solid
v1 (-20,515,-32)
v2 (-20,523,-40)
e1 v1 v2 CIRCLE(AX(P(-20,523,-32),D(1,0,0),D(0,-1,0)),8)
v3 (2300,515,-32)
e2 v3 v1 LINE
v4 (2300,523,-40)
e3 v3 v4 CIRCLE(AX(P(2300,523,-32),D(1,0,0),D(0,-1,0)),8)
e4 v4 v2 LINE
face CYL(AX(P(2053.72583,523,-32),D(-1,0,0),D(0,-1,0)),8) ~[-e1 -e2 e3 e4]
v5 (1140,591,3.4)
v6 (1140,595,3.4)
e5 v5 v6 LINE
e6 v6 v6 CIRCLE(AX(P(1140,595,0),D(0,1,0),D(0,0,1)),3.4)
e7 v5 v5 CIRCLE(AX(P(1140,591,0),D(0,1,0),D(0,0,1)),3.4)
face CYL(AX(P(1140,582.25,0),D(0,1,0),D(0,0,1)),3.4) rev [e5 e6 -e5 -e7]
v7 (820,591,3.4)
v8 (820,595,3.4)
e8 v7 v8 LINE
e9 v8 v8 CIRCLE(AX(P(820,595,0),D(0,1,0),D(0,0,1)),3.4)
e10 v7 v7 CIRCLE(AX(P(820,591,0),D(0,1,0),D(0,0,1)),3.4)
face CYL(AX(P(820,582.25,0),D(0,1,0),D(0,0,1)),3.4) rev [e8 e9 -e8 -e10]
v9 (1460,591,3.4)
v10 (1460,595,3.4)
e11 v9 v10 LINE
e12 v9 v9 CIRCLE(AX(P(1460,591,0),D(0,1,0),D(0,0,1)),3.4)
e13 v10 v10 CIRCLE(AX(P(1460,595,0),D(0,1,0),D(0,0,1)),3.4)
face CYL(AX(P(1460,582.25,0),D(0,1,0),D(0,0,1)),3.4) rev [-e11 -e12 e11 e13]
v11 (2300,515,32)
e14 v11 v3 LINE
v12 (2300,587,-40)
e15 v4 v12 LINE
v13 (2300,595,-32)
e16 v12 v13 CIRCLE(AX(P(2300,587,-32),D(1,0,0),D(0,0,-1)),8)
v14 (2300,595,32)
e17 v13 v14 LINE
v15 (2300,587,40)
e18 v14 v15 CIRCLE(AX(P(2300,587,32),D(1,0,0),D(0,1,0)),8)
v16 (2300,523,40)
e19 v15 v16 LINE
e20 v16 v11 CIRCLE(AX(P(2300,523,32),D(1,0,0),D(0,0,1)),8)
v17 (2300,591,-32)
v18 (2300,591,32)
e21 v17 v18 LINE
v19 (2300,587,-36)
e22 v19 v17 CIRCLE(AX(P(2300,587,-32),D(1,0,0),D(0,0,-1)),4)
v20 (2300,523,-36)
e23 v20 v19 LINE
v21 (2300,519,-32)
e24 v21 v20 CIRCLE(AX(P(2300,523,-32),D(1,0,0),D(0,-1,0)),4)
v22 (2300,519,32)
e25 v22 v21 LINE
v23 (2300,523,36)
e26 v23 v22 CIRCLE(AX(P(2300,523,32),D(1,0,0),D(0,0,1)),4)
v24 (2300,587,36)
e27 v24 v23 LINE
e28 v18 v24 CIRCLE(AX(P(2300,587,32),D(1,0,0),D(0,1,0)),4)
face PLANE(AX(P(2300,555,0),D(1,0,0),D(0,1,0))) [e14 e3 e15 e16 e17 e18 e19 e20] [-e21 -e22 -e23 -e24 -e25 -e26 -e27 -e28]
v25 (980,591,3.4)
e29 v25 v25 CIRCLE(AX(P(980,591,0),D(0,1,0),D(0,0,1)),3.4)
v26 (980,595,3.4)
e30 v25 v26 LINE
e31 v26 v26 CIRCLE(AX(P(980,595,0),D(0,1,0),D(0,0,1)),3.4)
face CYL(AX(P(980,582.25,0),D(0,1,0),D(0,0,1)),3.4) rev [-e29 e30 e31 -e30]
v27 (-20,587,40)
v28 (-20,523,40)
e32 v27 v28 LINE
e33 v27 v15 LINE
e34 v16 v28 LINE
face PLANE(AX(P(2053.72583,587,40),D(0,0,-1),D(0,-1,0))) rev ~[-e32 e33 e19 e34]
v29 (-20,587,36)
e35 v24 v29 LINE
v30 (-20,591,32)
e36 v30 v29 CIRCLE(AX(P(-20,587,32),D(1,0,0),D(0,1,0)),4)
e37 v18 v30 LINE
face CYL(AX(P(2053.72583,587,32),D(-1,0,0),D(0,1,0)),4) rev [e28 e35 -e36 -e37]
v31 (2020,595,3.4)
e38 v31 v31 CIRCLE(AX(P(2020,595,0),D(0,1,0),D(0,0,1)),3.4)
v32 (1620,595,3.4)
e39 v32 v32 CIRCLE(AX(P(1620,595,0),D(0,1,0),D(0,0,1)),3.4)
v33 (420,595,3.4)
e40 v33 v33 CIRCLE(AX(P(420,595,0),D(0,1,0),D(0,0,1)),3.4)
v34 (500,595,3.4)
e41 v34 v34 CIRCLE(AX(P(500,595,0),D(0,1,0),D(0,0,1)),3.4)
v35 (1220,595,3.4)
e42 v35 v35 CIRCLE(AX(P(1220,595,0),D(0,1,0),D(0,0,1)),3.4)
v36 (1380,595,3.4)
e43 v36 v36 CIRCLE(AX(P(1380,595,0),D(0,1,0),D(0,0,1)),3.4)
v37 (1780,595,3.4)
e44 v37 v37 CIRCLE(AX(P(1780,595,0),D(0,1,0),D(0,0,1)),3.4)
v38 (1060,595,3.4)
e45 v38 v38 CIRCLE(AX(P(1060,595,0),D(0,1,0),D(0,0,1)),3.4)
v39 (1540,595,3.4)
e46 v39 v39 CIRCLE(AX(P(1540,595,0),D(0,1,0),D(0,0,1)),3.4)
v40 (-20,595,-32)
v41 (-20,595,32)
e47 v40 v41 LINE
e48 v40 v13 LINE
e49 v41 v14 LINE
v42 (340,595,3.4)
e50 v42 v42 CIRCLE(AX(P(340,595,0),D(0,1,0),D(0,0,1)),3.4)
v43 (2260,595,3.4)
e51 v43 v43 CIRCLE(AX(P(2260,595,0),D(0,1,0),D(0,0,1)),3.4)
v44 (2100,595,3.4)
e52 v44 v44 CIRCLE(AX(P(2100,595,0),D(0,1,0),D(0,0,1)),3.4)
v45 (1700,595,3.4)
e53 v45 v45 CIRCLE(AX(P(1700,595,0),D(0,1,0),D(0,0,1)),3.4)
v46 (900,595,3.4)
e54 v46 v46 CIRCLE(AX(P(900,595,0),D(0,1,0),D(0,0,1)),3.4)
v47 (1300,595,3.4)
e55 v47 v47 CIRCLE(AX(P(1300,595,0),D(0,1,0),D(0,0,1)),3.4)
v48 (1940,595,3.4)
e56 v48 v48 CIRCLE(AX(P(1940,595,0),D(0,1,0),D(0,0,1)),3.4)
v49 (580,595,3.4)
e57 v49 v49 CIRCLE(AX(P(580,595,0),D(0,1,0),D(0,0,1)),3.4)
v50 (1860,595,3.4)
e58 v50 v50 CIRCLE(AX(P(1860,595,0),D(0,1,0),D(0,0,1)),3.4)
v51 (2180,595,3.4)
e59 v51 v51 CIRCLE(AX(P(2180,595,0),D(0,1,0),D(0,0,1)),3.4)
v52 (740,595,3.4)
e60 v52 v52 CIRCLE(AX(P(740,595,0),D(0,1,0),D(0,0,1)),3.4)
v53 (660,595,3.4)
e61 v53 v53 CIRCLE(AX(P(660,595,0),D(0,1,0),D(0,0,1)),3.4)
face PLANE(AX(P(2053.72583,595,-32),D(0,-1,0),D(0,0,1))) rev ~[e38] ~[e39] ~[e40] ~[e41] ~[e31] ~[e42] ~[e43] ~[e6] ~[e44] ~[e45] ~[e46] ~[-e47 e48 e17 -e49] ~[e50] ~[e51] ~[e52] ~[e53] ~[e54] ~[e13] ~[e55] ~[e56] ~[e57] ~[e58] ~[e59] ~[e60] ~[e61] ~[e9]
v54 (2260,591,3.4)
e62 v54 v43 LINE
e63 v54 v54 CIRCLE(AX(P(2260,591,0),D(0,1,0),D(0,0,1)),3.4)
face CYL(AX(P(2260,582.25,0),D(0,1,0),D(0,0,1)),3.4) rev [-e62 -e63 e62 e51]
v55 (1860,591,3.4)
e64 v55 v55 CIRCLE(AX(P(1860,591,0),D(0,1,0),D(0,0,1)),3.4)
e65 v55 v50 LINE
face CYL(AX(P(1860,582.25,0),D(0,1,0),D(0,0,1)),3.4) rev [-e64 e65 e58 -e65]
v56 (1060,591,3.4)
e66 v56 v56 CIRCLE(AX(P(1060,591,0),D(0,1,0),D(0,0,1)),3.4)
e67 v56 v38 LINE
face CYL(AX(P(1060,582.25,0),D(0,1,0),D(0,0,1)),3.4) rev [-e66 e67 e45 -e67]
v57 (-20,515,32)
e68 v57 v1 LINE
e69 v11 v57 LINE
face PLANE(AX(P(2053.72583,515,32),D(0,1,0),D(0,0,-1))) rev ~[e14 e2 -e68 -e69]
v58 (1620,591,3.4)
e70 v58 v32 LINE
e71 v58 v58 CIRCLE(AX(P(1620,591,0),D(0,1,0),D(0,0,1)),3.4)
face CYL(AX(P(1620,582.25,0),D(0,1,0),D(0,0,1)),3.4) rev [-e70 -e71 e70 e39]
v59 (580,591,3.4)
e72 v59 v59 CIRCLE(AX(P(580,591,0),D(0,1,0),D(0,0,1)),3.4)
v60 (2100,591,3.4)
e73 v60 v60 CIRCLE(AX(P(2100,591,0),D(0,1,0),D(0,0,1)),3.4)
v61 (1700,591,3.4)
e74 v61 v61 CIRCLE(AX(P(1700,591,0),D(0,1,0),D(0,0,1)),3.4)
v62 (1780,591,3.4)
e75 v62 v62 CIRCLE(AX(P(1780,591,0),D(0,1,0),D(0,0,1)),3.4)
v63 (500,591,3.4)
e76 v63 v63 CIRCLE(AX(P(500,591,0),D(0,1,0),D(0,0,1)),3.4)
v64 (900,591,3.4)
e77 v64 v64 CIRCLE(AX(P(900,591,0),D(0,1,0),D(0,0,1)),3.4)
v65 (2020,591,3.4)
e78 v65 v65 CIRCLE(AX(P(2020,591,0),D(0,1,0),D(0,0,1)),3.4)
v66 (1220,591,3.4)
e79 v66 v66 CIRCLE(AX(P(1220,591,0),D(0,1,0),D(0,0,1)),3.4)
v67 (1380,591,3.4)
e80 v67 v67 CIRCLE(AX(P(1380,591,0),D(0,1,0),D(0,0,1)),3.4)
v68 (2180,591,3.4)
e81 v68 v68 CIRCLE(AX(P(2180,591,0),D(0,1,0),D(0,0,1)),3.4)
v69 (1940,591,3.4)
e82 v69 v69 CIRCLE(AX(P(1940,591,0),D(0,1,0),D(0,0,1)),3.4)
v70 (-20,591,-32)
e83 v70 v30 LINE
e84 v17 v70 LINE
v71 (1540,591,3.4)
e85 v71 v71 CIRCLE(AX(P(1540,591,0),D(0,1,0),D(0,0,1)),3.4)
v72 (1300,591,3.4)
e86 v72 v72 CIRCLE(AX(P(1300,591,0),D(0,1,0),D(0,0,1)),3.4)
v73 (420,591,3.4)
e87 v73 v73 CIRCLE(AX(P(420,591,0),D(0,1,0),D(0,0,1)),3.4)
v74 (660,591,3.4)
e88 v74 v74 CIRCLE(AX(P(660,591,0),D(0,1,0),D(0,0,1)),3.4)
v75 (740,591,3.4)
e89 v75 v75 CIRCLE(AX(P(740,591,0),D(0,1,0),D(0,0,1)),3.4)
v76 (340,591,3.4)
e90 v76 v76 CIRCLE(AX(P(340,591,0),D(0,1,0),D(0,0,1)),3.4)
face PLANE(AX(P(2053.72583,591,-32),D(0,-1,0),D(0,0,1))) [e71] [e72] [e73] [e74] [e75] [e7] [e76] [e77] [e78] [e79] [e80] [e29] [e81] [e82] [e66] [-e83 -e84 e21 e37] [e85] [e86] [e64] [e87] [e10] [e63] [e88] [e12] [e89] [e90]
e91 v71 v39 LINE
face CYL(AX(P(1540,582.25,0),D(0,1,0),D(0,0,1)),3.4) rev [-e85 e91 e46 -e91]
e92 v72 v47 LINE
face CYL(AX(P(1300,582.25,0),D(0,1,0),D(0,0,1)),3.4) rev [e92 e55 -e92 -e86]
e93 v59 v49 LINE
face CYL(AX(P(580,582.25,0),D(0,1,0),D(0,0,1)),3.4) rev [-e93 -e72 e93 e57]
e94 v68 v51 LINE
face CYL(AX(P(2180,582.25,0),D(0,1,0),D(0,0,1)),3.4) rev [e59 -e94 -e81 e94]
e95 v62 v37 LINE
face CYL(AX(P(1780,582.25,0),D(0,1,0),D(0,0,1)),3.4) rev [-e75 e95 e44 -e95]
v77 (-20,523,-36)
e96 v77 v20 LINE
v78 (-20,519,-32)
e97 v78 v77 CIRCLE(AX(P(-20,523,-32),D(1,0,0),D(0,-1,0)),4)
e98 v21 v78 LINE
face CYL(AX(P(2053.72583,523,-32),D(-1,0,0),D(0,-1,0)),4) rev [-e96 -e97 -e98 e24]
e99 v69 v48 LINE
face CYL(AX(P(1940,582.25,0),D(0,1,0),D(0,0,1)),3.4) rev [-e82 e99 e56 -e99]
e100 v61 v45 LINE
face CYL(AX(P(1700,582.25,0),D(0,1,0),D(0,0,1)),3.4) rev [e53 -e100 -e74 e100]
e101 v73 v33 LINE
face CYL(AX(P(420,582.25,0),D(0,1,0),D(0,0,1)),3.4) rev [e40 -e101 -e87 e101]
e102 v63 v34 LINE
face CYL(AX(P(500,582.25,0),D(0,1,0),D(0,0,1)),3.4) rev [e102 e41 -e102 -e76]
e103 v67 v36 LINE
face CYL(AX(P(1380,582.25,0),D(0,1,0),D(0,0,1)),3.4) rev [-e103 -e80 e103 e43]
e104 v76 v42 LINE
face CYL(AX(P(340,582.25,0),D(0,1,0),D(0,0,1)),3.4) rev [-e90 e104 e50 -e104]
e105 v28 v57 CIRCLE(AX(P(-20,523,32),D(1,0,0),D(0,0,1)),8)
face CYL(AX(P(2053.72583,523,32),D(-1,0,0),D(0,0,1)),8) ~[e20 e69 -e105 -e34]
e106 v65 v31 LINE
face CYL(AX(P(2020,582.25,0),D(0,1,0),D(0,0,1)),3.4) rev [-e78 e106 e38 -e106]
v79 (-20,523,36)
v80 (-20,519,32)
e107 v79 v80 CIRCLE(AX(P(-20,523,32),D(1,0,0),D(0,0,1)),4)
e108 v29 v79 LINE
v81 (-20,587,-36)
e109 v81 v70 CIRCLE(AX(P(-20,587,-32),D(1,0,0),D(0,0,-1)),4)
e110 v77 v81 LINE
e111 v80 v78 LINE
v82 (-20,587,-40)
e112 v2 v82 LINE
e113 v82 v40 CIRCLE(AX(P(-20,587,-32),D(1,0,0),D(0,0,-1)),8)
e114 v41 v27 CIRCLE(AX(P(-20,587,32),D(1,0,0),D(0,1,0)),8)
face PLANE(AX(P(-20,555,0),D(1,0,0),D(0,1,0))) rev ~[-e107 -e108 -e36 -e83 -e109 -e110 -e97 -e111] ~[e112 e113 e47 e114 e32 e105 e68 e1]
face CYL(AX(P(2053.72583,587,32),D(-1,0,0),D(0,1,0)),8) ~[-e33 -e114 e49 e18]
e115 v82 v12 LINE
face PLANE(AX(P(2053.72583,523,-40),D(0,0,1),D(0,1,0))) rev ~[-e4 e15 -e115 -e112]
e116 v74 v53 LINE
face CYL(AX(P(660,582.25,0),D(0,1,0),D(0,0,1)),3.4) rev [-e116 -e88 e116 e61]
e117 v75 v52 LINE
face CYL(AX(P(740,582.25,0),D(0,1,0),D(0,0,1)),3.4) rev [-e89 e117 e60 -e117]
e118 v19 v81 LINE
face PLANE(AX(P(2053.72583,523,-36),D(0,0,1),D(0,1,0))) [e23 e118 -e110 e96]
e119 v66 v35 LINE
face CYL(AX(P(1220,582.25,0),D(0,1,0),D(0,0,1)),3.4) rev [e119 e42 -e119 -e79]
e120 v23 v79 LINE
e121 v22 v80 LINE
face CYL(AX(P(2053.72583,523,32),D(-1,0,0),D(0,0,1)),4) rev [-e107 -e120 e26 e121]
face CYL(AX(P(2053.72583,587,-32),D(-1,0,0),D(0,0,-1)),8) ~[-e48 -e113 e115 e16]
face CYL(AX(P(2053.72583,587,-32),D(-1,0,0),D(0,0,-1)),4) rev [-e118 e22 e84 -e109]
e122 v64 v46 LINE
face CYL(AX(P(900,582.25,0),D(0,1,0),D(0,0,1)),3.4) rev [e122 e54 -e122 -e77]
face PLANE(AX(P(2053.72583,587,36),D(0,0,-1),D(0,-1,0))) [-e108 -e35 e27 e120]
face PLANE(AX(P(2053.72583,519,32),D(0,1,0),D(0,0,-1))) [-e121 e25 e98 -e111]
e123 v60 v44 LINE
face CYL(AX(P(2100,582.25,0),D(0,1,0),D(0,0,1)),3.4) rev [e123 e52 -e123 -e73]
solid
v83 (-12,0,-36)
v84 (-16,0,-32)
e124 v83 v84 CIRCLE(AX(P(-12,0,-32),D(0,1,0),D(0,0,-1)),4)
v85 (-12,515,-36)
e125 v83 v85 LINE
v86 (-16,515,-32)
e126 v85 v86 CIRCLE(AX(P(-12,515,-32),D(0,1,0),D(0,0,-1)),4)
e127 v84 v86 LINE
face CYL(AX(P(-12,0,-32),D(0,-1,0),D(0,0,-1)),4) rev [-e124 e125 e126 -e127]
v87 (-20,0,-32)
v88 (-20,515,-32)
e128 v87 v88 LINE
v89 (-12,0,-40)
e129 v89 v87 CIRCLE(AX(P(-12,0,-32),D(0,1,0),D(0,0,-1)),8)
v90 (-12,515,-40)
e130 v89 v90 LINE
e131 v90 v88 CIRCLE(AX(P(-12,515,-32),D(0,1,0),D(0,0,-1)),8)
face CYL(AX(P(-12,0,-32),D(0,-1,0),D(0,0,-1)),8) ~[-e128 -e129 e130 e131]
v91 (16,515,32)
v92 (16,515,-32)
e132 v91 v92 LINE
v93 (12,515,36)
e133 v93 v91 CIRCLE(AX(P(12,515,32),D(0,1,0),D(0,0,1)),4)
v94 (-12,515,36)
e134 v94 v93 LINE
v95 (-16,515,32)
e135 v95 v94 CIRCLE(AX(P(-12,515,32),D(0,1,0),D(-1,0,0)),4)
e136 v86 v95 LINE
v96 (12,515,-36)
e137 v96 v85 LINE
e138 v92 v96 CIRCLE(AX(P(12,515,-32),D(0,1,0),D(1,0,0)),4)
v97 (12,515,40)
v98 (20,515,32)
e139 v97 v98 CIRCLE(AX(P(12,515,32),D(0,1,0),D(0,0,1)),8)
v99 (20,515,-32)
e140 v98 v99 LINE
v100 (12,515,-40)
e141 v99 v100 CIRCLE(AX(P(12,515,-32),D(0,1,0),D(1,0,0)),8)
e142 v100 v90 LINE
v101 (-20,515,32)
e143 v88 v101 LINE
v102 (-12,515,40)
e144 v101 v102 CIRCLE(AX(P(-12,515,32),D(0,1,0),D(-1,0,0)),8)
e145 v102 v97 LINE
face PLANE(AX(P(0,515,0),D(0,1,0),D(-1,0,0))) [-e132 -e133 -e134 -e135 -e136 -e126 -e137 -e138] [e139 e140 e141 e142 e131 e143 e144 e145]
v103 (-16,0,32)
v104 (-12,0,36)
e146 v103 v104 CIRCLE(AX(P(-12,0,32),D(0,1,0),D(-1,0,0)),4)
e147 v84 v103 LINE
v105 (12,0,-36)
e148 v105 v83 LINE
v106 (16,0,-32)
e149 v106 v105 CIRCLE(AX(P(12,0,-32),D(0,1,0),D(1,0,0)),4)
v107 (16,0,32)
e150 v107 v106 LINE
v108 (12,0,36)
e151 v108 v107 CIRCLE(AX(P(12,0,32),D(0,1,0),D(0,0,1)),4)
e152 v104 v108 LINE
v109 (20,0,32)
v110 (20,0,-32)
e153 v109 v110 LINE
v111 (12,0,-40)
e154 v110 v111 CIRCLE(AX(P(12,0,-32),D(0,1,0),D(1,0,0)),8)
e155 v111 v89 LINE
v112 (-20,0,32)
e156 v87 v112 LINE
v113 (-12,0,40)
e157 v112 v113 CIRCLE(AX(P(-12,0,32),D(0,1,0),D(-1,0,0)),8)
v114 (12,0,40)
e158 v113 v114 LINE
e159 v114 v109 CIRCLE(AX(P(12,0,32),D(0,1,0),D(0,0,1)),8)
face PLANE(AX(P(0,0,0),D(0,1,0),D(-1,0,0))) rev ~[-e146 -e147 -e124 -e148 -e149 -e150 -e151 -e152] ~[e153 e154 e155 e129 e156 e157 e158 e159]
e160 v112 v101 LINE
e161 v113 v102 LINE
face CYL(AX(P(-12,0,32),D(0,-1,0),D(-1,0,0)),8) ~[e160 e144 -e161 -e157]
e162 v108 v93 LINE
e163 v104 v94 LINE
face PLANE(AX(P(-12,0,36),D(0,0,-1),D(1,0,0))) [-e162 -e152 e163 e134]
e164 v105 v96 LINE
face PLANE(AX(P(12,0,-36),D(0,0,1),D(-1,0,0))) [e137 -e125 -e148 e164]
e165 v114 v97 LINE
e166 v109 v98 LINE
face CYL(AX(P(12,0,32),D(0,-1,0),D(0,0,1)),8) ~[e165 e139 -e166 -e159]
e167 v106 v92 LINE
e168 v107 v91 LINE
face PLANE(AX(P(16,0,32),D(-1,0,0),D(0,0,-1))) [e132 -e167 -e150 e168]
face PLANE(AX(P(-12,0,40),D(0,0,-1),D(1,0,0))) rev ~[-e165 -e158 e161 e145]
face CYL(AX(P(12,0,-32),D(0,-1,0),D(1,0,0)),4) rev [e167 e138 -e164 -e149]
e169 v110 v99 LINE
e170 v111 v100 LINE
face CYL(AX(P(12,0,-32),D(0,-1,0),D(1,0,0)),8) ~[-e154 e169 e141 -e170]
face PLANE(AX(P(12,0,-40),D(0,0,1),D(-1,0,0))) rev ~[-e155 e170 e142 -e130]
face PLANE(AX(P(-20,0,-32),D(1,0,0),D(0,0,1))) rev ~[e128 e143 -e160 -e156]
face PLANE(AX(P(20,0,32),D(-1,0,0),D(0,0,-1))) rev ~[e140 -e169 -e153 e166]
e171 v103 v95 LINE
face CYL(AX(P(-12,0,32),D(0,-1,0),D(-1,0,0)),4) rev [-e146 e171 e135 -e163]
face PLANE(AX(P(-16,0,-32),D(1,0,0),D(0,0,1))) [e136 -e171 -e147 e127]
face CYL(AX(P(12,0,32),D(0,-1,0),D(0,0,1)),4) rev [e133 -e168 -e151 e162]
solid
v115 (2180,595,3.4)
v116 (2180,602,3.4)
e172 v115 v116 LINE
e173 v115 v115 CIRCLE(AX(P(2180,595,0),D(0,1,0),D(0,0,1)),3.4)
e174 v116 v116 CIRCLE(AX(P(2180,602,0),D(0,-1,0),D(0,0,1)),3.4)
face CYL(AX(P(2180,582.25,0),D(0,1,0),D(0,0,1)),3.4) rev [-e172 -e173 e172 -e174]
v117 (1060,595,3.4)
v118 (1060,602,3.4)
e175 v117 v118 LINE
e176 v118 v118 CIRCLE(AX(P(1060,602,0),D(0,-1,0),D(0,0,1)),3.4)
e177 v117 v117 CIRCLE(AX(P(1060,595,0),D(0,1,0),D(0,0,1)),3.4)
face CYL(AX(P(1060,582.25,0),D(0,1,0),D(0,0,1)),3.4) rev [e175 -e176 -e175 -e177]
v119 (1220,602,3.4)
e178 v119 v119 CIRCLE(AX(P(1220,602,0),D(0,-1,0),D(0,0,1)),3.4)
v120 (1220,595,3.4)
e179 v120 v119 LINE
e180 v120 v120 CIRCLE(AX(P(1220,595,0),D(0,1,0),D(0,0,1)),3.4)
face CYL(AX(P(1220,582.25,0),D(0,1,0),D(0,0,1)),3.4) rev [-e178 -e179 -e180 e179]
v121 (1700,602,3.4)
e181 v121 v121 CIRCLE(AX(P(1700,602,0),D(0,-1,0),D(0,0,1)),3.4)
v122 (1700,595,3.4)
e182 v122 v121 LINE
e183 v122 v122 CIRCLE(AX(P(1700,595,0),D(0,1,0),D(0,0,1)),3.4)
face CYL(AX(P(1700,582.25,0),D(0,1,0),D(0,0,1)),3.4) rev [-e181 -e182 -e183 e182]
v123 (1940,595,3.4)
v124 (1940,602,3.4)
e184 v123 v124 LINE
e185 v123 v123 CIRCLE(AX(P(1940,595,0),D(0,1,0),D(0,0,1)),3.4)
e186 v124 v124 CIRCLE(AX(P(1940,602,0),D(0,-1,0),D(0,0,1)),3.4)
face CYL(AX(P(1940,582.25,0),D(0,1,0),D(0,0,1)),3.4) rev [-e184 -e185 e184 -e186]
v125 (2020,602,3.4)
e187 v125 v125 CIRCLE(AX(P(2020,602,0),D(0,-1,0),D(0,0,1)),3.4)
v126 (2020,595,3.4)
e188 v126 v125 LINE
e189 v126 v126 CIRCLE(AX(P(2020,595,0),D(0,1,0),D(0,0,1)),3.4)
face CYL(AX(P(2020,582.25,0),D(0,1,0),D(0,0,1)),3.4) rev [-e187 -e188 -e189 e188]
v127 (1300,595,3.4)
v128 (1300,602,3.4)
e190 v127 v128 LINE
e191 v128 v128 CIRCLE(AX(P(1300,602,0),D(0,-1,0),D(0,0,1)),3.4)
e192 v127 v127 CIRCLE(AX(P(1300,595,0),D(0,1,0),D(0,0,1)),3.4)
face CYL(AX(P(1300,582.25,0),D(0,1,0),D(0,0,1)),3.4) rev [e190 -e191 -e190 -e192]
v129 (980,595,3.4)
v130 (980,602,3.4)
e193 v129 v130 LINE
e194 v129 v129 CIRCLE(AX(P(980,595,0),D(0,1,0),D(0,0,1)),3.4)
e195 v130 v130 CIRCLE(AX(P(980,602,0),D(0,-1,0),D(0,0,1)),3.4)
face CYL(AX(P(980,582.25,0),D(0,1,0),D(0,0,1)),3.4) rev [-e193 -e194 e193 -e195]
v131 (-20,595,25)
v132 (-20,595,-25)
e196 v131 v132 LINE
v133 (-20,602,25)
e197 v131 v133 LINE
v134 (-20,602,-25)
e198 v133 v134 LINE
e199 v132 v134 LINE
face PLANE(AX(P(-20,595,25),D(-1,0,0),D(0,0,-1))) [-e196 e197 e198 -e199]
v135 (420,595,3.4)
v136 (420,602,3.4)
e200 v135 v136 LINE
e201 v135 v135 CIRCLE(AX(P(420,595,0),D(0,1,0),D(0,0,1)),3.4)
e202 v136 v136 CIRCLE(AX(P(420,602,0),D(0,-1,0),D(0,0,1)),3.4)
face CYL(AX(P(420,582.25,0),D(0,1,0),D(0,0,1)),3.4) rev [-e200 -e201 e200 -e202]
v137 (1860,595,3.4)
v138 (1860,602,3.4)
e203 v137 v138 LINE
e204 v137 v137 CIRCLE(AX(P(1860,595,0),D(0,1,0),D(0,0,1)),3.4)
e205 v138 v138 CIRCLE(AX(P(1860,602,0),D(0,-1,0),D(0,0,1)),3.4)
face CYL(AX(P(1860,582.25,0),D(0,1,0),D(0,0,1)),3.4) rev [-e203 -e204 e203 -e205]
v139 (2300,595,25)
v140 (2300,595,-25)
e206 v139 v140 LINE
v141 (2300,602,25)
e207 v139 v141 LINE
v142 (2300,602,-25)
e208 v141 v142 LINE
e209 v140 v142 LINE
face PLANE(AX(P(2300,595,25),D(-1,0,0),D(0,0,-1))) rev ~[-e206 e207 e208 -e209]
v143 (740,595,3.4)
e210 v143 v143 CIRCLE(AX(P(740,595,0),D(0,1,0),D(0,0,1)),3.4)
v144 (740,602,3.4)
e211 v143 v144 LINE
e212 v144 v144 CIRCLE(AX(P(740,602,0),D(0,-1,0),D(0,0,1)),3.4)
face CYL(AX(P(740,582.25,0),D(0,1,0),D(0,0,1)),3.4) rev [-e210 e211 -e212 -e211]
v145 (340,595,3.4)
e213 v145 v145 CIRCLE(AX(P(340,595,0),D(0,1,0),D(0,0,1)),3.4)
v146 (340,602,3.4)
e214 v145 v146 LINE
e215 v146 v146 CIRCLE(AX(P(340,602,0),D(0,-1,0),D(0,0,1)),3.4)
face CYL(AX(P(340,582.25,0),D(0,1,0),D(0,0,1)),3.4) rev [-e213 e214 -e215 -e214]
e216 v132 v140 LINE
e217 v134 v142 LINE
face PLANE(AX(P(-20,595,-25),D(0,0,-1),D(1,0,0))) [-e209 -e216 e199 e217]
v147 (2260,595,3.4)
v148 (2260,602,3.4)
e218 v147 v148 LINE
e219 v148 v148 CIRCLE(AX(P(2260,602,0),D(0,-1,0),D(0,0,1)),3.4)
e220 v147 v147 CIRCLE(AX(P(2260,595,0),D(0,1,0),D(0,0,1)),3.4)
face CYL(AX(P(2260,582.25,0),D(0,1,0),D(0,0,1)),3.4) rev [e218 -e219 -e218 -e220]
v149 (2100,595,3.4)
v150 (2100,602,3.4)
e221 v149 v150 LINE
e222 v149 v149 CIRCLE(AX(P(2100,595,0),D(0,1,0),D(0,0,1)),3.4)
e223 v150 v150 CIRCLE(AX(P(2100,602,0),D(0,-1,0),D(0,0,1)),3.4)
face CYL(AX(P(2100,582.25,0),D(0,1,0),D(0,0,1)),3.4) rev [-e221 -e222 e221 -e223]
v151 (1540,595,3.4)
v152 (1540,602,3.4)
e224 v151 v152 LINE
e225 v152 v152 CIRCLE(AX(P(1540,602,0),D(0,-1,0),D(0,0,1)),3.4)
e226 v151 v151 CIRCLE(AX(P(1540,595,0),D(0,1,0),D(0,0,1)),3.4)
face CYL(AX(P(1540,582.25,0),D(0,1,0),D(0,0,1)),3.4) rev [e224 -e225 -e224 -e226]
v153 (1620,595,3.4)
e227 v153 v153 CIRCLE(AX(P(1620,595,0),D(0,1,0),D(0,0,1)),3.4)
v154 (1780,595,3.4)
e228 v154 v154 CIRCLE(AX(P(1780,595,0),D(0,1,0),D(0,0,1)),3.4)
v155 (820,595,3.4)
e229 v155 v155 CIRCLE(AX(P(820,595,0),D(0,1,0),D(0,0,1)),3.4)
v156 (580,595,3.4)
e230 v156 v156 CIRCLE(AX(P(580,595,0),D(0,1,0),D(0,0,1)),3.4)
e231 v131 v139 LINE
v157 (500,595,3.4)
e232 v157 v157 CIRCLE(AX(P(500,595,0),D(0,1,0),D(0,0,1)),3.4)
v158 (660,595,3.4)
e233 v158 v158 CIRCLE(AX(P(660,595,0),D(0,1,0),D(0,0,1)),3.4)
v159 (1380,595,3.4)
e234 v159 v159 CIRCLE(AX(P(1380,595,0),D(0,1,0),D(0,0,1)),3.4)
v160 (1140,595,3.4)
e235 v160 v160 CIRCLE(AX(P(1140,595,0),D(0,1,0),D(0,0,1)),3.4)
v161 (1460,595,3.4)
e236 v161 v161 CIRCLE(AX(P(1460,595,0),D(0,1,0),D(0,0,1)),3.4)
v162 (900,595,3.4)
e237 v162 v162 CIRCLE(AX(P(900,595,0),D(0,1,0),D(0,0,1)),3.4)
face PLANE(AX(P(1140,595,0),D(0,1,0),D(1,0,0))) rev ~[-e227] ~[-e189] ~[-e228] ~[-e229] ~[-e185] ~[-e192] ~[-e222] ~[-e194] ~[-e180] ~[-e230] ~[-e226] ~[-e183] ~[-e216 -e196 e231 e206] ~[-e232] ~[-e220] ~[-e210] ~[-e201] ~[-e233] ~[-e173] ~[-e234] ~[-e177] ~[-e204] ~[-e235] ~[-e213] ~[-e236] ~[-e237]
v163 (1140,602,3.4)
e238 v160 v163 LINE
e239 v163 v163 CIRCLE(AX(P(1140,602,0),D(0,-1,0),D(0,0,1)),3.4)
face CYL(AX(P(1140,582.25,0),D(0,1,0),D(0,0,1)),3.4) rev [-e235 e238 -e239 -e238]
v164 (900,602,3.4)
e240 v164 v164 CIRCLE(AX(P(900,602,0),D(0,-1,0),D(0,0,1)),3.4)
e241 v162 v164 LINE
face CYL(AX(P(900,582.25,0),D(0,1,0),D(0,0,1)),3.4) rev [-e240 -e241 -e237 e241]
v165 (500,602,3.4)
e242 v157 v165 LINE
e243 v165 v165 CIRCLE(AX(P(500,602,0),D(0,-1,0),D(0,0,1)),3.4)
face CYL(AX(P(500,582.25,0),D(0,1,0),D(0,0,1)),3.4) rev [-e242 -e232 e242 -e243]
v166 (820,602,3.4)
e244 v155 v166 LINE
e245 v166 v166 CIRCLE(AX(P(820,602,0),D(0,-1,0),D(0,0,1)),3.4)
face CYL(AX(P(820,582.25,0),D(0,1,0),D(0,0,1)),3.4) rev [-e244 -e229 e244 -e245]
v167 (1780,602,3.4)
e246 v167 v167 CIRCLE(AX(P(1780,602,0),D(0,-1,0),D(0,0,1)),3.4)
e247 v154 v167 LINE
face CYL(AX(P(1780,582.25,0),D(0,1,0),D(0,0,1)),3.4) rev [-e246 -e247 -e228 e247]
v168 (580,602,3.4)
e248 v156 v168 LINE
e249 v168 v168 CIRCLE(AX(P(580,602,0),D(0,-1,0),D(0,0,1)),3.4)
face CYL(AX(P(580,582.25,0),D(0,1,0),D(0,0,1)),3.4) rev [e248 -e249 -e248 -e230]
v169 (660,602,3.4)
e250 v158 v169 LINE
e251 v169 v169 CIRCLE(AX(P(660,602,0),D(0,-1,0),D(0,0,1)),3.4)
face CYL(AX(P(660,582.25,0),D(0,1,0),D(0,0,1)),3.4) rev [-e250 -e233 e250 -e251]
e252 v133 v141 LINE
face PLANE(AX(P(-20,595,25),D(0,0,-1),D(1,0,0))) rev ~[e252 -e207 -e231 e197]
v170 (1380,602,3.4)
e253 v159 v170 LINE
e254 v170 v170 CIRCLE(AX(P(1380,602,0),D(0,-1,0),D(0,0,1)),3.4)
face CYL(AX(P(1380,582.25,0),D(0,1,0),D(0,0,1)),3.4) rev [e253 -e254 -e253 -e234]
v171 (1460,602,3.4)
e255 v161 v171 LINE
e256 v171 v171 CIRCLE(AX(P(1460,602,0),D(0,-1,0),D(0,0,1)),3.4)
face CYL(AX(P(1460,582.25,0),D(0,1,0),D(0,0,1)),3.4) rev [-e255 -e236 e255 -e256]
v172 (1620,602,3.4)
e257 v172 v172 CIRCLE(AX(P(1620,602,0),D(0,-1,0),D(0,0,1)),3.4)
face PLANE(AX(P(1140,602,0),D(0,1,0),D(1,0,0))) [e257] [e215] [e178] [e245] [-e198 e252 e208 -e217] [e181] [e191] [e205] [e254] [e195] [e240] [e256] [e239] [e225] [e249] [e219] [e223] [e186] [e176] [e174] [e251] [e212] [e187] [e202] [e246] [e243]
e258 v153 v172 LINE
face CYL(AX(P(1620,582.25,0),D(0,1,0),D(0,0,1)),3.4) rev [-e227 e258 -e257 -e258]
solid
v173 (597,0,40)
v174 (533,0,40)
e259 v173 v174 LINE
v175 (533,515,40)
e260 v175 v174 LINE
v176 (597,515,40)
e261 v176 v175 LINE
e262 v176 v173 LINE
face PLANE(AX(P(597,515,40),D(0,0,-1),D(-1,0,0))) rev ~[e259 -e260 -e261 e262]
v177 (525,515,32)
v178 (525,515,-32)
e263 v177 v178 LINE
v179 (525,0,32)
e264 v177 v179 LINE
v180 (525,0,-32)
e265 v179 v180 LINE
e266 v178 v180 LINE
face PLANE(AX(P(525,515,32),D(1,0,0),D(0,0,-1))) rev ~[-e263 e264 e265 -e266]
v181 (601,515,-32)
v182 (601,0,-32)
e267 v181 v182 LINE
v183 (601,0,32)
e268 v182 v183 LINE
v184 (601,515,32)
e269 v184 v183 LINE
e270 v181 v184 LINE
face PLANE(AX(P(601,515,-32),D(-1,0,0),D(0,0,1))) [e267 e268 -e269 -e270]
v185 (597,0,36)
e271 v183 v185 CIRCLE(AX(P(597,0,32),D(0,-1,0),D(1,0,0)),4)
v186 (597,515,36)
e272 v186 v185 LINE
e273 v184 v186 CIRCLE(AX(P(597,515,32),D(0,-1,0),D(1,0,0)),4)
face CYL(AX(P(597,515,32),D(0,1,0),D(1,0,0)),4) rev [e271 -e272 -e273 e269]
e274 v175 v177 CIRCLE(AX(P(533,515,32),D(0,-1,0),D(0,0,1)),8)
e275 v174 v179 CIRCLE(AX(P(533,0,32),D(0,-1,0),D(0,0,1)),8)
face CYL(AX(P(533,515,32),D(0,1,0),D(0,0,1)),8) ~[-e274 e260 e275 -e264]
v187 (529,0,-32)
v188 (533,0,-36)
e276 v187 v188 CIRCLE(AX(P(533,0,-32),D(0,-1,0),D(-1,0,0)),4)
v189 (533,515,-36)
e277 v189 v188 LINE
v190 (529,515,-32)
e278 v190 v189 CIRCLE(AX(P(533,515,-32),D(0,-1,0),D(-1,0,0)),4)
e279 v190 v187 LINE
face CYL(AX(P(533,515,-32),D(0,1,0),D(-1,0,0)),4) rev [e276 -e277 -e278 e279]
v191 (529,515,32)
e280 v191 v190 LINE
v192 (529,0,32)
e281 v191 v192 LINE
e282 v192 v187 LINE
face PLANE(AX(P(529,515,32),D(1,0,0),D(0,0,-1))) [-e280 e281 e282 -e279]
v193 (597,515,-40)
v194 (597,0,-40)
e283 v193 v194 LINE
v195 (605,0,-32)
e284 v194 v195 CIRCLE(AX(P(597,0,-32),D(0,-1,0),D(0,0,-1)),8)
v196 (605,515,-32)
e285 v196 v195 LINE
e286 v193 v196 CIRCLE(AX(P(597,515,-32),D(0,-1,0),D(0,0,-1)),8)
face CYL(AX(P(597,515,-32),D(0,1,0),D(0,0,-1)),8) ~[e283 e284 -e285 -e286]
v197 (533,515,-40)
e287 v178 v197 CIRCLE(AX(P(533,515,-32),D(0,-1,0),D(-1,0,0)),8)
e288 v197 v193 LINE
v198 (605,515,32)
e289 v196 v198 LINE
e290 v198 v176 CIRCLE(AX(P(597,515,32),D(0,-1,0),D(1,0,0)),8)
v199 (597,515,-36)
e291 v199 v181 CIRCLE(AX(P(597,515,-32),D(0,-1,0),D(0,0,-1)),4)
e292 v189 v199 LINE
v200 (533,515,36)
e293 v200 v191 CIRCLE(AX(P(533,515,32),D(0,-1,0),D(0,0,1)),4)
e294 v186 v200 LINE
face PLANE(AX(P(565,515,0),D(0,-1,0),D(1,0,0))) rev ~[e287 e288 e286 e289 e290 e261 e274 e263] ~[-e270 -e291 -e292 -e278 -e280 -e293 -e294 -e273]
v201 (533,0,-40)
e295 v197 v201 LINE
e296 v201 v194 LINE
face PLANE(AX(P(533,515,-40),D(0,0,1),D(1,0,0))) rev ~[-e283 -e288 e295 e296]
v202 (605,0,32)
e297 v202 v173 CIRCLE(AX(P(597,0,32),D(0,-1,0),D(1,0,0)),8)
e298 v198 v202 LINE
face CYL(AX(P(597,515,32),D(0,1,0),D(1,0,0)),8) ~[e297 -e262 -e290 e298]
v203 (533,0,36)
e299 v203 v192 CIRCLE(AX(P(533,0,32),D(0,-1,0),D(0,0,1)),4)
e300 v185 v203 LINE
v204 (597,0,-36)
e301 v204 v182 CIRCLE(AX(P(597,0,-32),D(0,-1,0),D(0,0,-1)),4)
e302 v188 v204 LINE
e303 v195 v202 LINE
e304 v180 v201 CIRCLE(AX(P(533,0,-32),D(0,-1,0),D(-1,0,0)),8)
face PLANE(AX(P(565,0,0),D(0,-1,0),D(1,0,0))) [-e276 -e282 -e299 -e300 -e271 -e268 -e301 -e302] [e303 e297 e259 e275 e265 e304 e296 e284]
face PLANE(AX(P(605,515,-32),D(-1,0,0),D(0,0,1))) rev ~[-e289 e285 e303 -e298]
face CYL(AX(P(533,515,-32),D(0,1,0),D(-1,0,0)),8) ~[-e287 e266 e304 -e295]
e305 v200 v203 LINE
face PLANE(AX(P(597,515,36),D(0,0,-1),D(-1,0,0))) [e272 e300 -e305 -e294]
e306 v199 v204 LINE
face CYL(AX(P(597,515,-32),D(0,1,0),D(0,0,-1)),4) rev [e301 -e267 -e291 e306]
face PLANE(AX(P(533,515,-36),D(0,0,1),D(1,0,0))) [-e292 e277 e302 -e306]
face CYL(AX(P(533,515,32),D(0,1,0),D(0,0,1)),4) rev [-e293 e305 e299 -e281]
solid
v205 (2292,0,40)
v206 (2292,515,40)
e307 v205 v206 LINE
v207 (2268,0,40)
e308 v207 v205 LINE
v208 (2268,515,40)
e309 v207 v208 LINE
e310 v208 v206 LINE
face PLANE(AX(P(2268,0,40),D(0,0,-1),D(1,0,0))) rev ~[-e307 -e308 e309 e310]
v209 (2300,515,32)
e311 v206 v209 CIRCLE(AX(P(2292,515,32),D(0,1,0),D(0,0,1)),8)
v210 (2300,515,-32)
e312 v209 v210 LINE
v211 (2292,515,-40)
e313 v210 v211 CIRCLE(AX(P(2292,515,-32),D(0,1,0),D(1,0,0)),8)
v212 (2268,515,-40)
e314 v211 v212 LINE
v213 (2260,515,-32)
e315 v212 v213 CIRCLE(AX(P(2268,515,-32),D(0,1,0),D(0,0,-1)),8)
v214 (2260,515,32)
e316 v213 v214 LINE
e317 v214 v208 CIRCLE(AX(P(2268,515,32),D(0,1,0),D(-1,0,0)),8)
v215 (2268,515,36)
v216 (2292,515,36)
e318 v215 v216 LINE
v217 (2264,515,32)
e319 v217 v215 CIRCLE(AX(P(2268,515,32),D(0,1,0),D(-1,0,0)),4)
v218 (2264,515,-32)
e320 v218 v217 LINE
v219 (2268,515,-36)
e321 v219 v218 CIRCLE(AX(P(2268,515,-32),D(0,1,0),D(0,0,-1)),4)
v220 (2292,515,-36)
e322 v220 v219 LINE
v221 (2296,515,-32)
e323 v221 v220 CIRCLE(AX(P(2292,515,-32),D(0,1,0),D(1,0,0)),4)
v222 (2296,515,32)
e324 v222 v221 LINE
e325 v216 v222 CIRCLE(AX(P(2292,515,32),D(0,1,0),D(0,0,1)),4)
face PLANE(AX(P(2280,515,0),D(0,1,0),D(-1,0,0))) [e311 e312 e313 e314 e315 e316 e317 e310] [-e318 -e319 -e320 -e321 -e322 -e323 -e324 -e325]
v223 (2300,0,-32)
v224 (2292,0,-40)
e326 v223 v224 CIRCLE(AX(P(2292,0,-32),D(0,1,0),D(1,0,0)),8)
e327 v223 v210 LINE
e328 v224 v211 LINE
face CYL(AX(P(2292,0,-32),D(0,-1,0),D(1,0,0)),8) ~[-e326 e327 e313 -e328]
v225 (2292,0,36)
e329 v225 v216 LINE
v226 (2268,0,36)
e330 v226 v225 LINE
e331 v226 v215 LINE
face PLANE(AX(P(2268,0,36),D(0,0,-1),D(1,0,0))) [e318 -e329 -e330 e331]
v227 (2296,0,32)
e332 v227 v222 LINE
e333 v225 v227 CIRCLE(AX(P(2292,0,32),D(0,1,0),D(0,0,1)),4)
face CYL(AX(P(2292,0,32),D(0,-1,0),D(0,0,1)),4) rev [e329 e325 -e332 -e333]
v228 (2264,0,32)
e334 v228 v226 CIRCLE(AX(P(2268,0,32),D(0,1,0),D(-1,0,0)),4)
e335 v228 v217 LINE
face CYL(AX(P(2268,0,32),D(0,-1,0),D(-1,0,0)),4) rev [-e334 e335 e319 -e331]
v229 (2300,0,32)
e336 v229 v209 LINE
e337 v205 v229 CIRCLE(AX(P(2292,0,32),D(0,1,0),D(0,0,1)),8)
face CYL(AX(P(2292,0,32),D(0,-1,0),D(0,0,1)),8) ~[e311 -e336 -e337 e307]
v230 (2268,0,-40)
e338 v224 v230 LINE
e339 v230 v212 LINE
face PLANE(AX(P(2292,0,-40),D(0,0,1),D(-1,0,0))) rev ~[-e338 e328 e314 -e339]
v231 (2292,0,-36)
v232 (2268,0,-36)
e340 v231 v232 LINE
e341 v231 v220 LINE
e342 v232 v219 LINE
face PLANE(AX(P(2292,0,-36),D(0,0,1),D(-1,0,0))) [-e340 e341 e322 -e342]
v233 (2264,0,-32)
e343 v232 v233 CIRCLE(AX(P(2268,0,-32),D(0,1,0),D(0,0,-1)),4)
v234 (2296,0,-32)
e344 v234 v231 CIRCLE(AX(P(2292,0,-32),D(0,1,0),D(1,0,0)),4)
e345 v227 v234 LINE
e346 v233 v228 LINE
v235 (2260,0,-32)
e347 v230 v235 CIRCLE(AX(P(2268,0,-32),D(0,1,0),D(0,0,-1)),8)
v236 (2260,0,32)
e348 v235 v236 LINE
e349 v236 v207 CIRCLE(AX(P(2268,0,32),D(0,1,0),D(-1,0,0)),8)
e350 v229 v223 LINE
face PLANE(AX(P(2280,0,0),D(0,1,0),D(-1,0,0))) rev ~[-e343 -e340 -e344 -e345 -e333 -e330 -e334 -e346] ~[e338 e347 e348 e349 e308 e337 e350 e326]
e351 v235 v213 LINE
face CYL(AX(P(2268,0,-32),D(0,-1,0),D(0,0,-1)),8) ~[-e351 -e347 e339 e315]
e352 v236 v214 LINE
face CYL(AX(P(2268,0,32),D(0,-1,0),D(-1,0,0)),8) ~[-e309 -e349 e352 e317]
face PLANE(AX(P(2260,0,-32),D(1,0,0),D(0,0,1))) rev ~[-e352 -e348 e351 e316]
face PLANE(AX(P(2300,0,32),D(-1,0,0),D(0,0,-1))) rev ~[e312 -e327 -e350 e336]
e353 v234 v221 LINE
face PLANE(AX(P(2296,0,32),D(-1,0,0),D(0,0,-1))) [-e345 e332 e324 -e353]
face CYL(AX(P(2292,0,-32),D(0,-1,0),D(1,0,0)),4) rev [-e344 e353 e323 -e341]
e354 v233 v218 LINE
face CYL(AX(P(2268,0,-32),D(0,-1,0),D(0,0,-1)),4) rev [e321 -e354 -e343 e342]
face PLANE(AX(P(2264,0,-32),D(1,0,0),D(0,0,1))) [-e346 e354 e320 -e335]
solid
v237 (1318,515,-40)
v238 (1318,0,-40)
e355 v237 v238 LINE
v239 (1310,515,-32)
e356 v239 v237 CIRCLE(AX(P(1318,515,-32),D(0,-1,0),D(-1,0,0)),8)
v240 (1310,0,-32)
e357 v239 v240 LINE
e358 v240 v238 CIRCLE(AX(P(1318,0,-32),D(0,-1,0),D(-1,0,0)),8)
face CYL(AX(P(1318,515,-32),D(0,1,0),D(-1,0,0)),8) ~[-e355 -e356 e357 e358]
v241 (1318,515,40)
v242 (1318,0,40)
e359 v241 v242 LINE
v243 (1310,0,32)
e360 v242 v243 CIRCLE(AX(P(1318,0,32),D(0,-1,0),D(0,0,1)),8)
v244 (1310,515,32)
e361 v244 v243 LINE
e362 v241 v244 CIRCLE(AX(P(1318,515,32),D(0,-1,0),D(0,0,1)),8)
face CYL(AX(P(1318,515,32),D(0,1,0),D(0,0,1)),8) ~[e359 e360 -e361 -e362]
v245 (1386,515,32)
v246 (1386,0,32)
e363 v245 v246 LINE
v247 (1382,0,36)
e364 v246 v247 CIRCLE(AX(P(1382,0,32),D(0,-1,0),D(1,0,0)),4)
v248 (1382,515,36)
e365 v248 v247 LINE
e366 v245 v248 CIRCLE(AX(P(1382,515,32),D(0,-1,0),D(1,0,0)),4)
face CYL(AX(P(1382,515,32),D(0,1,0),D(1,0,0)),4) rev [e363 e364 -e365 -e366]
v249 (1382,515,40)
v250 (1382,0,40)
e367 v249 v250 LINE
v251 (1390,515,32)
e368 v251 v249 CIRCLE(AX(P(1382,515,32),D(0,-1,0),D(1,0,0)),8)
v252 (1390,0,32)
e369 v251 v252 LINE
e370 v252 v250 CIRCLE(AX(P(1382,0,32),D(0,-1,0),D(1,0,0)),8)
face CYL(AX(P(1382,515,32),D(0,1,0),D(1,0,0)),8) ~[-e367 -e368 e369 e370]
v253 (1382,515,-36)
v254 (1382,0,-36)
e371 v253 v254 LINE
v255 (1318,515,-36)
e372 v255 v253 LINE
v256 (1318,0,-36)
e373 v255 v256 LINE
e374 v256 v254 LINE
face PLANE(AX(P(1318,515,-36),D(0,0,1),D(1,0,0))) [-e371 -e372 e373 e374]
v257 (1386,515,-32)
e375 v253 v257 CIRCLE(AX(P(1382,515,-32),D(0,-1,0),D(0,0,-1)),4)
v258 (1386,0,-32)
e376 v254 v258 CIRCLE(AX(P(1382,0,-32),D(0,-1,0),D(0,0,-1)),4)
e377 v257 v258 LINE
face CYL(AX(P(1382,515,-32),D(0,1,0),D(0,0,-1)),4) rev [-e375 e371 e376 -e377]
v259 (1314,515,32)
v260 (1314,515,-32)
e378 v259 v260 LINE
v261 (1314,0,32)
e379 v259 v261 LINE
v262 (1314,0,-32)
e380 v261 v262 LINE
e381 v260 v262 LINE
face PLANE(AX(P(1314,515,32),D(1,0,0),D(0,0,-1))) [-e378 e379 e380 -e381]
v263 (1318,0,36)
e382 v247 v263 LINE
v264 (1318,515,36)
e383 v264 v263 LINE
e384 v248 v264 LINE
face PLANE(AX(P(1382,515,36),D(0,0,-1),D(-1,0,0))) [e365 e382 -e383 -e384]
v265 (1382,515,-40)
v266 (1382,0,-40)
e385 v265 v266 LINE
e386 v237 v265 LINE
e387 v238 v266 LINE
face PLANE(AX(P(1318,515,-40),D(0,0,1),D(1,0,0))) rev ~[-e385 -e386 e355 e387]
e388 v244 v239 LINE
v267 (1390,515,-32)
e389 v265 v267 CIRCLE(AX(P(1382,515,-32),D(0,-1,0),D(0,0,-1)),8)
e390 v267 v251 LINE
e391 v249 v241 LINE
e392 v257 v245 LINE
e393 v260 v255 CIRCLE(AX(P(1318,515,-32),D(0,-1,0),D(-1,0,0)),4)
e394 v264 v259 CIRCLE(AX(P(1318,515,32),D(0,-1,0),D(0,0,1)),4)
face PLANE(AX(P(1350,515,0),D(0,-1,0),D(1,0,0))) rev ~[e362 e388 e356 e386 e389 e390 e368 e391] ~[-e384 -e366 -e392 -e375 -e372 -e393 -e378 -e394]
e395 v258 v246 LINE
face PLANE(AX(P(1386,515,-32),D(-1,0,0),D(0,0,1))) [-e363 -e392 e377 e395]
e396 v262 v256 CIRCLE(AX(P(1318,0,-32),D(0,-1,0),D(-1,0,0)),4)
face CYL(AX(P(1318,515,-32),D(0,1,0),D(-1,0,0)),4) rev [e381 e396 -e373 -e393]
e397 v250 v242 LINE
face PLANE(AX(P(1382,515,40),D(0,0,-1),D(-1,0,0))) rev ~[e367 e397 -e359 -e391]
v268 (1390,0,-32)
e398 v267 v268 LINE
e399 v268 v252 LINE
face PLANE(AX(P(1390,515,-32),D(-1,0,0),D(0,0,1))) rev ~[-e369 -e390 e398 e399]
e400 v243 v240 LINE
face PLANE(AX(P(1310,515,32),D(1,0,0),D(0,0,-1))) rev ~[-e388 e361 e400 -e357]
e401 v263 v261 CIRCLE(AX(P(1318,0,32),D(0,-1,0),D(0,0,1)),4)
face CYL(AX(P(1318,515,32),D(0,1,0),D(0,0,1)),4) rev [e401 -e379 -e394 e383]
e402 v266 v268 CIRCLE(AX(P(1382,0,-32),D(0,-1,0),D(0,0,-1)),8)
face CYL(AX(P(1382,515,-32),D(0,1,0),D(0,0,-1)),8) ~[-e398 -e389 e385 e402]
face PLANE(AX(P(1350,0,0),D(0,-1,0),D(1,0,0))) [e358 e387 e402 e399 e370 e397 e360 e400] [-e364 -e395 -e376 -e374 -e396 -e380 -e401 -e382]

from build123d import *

# Parameters (mm, degrees)
GB_6728_1986_RECTANGULAR_HOLLOW_SECTION_DEPTH  = 515
GB_6728_1986_RECTANGULAR_HOLLOW_SECT_2_DEPTH   = 515
GB_6728_1986_SQUARE_HOLLOW_SECTION_080_X_DEPTH = 2280
BODY_START                                     = 226.27416998
BODY_3_RUN_ON_DEPTH                            = 246.27416998
BODY_START_2                                   = 2053.72583002
BODY_3_RUN_ON_2_DEPTH                          = 246.27416998
SKETCH2_W                                      = 2320
SKETCH2_H                                      = 50
BOSS_EXTRUDE1_DEPTH                            = 10
SKETCH4_W                                      = 2320
SKETCH4_H                                      = 50
CUT_EXTRUDE1_DEPTH                             = 3
LPATTERN1_COUNT                                = 25
LPATTERN1_PITCH                                = 80
SQUARE_TUBE_80_X_80_X_4_0_1_DEPTH              = 515
SQUARE_TUBE_80_X_80_X_4_0_1_2_DEPTH            = 515


with BuildPart() as part:
    # Sketch11 → Gb／6728-1986 Rectangular Hollow Section 080 X 40 X 4(1) (new body)
    with BuildSketch(Plane(origin=(0, 0, 0), x_dir=(-1, 0, 0), z_dir=(0, 1, 0))):
        with BuildLine():
            Line((-12, -40), (12, -40))
            ThreePointArc((12, -40), (17.656854249, -37.656854249), (20, -32))
            Line((20, -32), (20, 32))
            ThreePointArc((20, 32), (17.656854249, 37.656854249), (12, 40))
            Line((12, 40), (-12, 40))
            ThreePointArc((-12, 40), (-17.656854249, 37.656854249), (-20, 32))
            Line((-20, 32), (-20, -32))
            ThreePointArc((-20, -32), (-17.656854249, -37.656854249), (-12, -40))
        make_face()
        with BuildLine():
            Line((-12, -36), (12, -36))
            ThreePointArc((12, -36), (14.828427125, -34.828427125), (16, -32))
            Line((16, -32), (16, 32))
            ThreePointArc((16, 32), (14.828427125, 34.828427125), (12, 36))
            Line((12, 36), (-12, 36))
            ThreePointArc((-12, 36), (-14.828427125, 34.828427125), (-16, 32))
            Line((-16, 32), (-16, -32))
            ThreePointArc((-16, -32), (-14.828427125, -34.828427125), (-12, -36))
        make_face(mode=Mode.SUBTRACT)
    extrude(amount=GB_6728_1986_RECTANGULAR_HOLLOW_SECTION_DEPTH)


with BuildPart() as body_2:
    # Sketch11 on segment 2 (carried to segment 2) → Gb_6728-1986 Rectangular Hollow Sect 2 (new body)
    with BuildSketch(Plane(origin=(2280, 0, 0), x_dir=(-1, 0, 0), z_dir=(0, 1, 0))):
        with BuildLine():
            Line((-12, -40), (12, -40))
            ThreePointArc((12, -40), (17.656854249, -37.656854249), (20, -32))
            Line((20, -32), (20, 32))
            ThreePointArc((20, 32), (17.656854249, 37.656854249), (12, 40))
            Line((12, 40), (-12, 40))
            ThreePointArc((-12, 40), (-17.656854249, 37.656854249), (-20, 32))
            Line((-20, 32), (-20, -32))
            ThreePointArc((-20, -32), (-17.656854249, -37.656854249), (-12, -40))
        make_face()
        with BuildLine():
            Line((-12, -36), (12, -36))
            ThreePointArc((12, -36), (14.828427125, -34.828427125), (16, -32))
            Line((16, -32), (16, 32))
            ThreePointArc((16, 32), (14.828427125, 34.828427125), (12, 36))
            Line((12, 36), (-12, 36))
            ThreePointArc((-12, 36), (-14.828427125, 34.828427125), (-16, 32))
            Line((-16, 32), (-16, -32))
            ThreePointArc((-16, -32), (-14.828427125, -34.828427125), (-12, -36))
        make_face(mode=Mode.SUBTRACT)
    extrude(amount=GB_6728_1986_RECTANGULAR_HOLLOW_SECT_2_DEPTH)


with BuildPart() as body_3:
    # Sketch1 → Gb／6728-1986 Square Hollow Section 080 X 80 X 4(1) (new body)
    with BuildSketch(Plane(origin=(0, 555, 0), x_dir=(0, 1, 0), z_dir=(1, 0, 0))):
        with BuildLine():
            Line((-32, -40), (32, -40))
            ThreePointArc((32, -40), (37.656854249, -37.656854249), (40, -32))
            Line((40, -32), (40, 32))
            ThreePointArc((40, 32), (37.656854249, 37.656854249), (32, 40))
            Line((32, 40), (-32, 40))
            ThreePointArc((-32, 40), (-37.656854249, 37.656854249), (-40, 32))
            Line((-40, 32), (-40, -32))
            ThreePointArc((-40, -32), (-37.656854249, -37.656854249), (-32, -40))
        make_face()
        with BuildLine():
            Line((-32, -36), (32, -36))
            ThreePointArc((32, -36), (34.828427125, -34.828427125), (36, -32))
            Line((36, -32), (36, 32))
            ThreePointArc((36, 32), (34.828427125, 34.828427125), (32, 36))
            Line((32, 36), (-32, 36))
            ThreePointArc((-32, 36), (-34.828427125, 34.828427125), (-36, 32))
            Line((-36, 32), (-36, -32))
            ThreePointArc((-36, -32), (-34.828427125, -34.828427125), (-32, -36))
        make_face(mode=Mode.SUBTRACT)
    extrude(amount=GB_6728_1986_SQUARE_HOLLOW_SECTION_080_X_DEPTH)

    # body 3 cut square before the run-on
    split(bisect_by=Plane(origin=(226.27416998, 555, 0), x_dir=(0, 1, 0), z_dir=(1, 0, 0)), keep=Keep.TOP)

    # Sketch1 → body 3 run on (add)
    with BuildSketch(Plane(origin=(0, 555, 0), x_dir=(0, 1, 0), z_dir=(1, 0, 0)).offset(BODY_START)):
        with BuildLine():
            Line((-32, -40), (32, -40))
            ThreePointArc((32, -40), (37.656854249, -37.656854249), (40, -32))
            Line((40, -32), (40, 32))
            ThreePointArc((40, 32), (37.656854249, 37.656854249), (32, 40))
            Line((32, 40), (-32, 40))
            ThreePointArc((-32, 40), (-37.656854249, 37.656854249), (-40, 32))
            Line((-40, 32), (-40, -32))
            ThreePointArc((-40, -32), (-37.656854249, -37.656854249), (-32, -40))
        make_face()
        with BuildLine():
            Line((-32, -36), (32, -36))
            ThreePointArc((32, -36), (34.828427125, -34.828427125), (36, -32))
            Line((36, -32), (36, 32))
            ThreePointArc((36, 32), (34.828427125, 34.828427125), (32, 36))
            Line((32, 36), (-32, 36))
            ThreePointArc((-32, 36), (-34.828427125, 34.828427125), (-36, 32))
            Line((-36, 32), (-36, -32))
            ThreePointArc((-36, -32), (-34.828427125, -34.828427125), (-32, -36))
        make_face(mode=Mode.SUBTRACT)
    extrude(amount=-BODY_3_RUN_ON_DEPTH)

    # body 3 cut square before the run-on
    split(bisect_by=Plane(origin=(2053.72583002, 555, 0), x_dir=(0, -1, 0), z_dir=(-1, 0, 0)), keep=Keep.TOP)

    # Sketch1 → body 3 run on 2 (add)
    with BuildSketch(Plane(origin=(0, 555, 0), x_dir=(0, 1, 0), z_dir=(1, 0, 0)).offset(BODY_START_2)):
        with BuildLine():
            Line((-32, -40), (32, -40))
            ThreePointArc((32, -40), (37.656854249, -37.656854249), (40, -32))
            Line((40, -32), (40, 32))
            ThreePointArc((40, 32), (37.656854249, 37.656854249), (32, 40))
            Line((32, 40), (-32, 40))
            ThreePointArc((-32, 40), (-37.656854249, 37.656854249), (-40, 32))
            Line((-40, 32), (-40, -32))
            ThreePointArc((-40, -32), (-37.656854249, -37.656854249), (-32, -40))
        make_face()
        with BuildLine():
            Line((-32, -36), (32, -36))
            ThreePointArc((32, -36), (34.828427125, -34.828427125), (36, -32))
            Line((36, -32), (36, 32))
            ThreePointArc((36, 32), (34.828427125, 34.828427125), (32, 36))
            Line((32, 36), (-32, 36))
            ThreePointArc((-32, 36), (-34.828427125, 34.828427125), (-36, 32))
            Line((-36, 32), (-36, -32))
            ThreePointArc((-36, -32), (-34.828427125, -34.828427125), (-32, -36))
        make_face(mode=Mode.SUBTRACT)
    extrude(amount=BODY_3_RUN_ON_2_DEPTH)


with BuildPart() as body_4:
    # Sketch2 → Boss-Extrude1 (new body)
    with BuildSketch(Plane(origin=(0, 595, 0), x_dir=(1, 0, 0), z_dir=(0, 1, 0))):
        with Locations((1140, 0)):
            Rectangle(SKETCH2_W, SKETCH2_H)
    extrude(amount=BOSS_EXTRUDE1_DEPTH)

    # Sketch4 → Cut-Extrude1 (cut)
    with BuildSketch(Plane(origin=(0, 605, 0), x_dir=(1, 0, 0), z_dir=(0, 1, 0))):
        with Locations((1140, 0)):
            Rectangle(SKETCH4_W, SKETCH4_H)
    extrude(amount=-CUT_EXTRUDE1_DEPTH, mode=Mode.SUBTRACT)


with BuildPart() as m8_tapped_hole1_tool:
    # Sketch6 → M8 Tapped Hole1 (revolve)
    with BuildSketch(Plane(origin=(2260, 602, 0), x_dir=(0, 0, 1), z_dir=(1, 0, 0))):
        Polygon((0, 0), (0, 21.792926105), (3.4, 19.75), (3.4, 0), align=None)
    m8_tapped_hole1 = revolve(axis=Axis((2260, 608.35, 0), (0, -1, 0)))


with BuildPart() as body_3_1:
    add(body_3.part)

    # M8 Tapped Hole1: cut by m8_tapped_hole1_tool
    add(m8_tapped_hole1_tool.part, mode=Mode.SUBTRACT)


with BuildPart() as body_4_1:
    add(body_4.part)

    # M8 Tapped Hole1: cut by m8_tapped_hole1_tool
    add(m8_tapped_hole1_tool.part, mode=Mode.SUBTRACT)


with BuildPart() as lpattern1_tool:
    # LPattern1: M8 Tapped Hole1 ×25
    with Locations(*[(-i * LPATTERN1_PITCH, 0, 0) for i in range(1, LPATTERN1_COUNT)]):
        add(m8_tapped_hole1)


with BuildPart() as body_3_2:
    add(body_3_1.part)

    # LPattern1: cut by lpattern1_tool
    add(lpattern1_tool.part, mode=Mode.SUBTRACT)


with BuildPart() as body_4_2:
    add(body_4_1.part)

    # LPattern1: cut by lpattern1_tool
    add(lpattern1_tool.part, mode=Mode.SUBTRACT)


with BuildPart() as body_5:
    # Sketch12 → Square Tube 80 X 80 X 4.0(1) (new body)
    with BuildSketch(Plane(origin=(565, 515, 0), x_dir=(1, 0, 0), z_dir=(0, -1, 0))):
        with BuildLine():
            Line((-32, -40), (32, -40))
            ThreePointArc((32, -40), (37.656854249, -37.656854249), (40, -32))
            Line((40, -32), (40, 32))
            ThreePointArc((40, 32), (37.656854249, 37.656854249), (32, 40))
            Line((32, 40), (-32, 40))
            ThreePointArc((-32, 40), (-37.656854249, 37.656854249), (-40, 32))
            Line((-40, 32), (-40, -32))
            ThreePointArc((-40, -32), (-37.656854249, -37.656854249), (-32, -40))
        make_face()
        with BuildLine():
            Line((-32, -36), (32, -36))
            ThreePointArc((32, -36), (34.828427125, -34.828427125), (36, -32))
            Line((36, -32), (36, 32))
            ThreePointArc((36, 32), (34.828427125, 34.828427125), (32, 36))
            Line((32, 36), (-32, 36))
            ThreePointArc((-32, 36), (-34.828427125, 34.828427125), (-36, 32))
            Line((-36, 32), (-36, -32))
            ThreePointArc((-36, -32), (-34.828427125, -34.828427125), (-32, -36))
        make_face(mode=Mode.SUBTRACT)
    extrude(amount=SQUARE_TUBE_80_X_80_X_4_0_1_DEPTH)


with BuildPart() as body_6:
    # Sketch12 on segment 2 (carried to segment 2) → Square Tube 80 X 80 X 4.0_1 2 (new body)
    with BuildSketch(Plane(origin=(1350, 515, 0), x_dir=(1, 0, 0), z_dir=(0, -1, 0))):
        with BuildLine():
            Line((-32, -40), (32, -40))
            ThreePointArc((32, -40), (37.656854249, -37.656854249), (40, -32))
            Line((40, -32), (40, 32))
            ThreePointArc((40, 32), (37.656854249, 37.656854249), (32, 40))
            Line((32, 40), (-32, 40))
            ThreePointArc((-32, 40), (-37.656854249, 37.656854249), (-40, 32))
            Line((-40, 32), (-40, -32))
            ThreePointArc((-40, -32), (-37.656854249, -37.656854249), (-32, -40))
        make_face()
        with BuildLine():
            Line((-32, -36), (32, -36))
            ThreePointArc((32, -36), (34.828427125, -34.828427125), (36, -32))
            Line((36, -32), (36, 32))
            ThreePointArc((36, 32), (34.828427125, 34.828427125), (32, 36))
            Line((32, 36), (-32, 36))
            ThreePointArc((-32, 36), (-34.828427125, 34.828427125), (-36, 32))
            Line((-36, 32), (-36, -32))
            ThreePointArc((-36, -32), (-34.828427125, -34.828427125), (-32, -36))
        make_face(mode=Mode.SUBTRACT)
    extrude(amount=SQUARE_TUBE_80_X_80_X_4_0_1_2_DEPTH)


solid = Compound([part.part, body_2.part, body_3_2.part, body_4_2.part, body_5.part, body_6.part])
